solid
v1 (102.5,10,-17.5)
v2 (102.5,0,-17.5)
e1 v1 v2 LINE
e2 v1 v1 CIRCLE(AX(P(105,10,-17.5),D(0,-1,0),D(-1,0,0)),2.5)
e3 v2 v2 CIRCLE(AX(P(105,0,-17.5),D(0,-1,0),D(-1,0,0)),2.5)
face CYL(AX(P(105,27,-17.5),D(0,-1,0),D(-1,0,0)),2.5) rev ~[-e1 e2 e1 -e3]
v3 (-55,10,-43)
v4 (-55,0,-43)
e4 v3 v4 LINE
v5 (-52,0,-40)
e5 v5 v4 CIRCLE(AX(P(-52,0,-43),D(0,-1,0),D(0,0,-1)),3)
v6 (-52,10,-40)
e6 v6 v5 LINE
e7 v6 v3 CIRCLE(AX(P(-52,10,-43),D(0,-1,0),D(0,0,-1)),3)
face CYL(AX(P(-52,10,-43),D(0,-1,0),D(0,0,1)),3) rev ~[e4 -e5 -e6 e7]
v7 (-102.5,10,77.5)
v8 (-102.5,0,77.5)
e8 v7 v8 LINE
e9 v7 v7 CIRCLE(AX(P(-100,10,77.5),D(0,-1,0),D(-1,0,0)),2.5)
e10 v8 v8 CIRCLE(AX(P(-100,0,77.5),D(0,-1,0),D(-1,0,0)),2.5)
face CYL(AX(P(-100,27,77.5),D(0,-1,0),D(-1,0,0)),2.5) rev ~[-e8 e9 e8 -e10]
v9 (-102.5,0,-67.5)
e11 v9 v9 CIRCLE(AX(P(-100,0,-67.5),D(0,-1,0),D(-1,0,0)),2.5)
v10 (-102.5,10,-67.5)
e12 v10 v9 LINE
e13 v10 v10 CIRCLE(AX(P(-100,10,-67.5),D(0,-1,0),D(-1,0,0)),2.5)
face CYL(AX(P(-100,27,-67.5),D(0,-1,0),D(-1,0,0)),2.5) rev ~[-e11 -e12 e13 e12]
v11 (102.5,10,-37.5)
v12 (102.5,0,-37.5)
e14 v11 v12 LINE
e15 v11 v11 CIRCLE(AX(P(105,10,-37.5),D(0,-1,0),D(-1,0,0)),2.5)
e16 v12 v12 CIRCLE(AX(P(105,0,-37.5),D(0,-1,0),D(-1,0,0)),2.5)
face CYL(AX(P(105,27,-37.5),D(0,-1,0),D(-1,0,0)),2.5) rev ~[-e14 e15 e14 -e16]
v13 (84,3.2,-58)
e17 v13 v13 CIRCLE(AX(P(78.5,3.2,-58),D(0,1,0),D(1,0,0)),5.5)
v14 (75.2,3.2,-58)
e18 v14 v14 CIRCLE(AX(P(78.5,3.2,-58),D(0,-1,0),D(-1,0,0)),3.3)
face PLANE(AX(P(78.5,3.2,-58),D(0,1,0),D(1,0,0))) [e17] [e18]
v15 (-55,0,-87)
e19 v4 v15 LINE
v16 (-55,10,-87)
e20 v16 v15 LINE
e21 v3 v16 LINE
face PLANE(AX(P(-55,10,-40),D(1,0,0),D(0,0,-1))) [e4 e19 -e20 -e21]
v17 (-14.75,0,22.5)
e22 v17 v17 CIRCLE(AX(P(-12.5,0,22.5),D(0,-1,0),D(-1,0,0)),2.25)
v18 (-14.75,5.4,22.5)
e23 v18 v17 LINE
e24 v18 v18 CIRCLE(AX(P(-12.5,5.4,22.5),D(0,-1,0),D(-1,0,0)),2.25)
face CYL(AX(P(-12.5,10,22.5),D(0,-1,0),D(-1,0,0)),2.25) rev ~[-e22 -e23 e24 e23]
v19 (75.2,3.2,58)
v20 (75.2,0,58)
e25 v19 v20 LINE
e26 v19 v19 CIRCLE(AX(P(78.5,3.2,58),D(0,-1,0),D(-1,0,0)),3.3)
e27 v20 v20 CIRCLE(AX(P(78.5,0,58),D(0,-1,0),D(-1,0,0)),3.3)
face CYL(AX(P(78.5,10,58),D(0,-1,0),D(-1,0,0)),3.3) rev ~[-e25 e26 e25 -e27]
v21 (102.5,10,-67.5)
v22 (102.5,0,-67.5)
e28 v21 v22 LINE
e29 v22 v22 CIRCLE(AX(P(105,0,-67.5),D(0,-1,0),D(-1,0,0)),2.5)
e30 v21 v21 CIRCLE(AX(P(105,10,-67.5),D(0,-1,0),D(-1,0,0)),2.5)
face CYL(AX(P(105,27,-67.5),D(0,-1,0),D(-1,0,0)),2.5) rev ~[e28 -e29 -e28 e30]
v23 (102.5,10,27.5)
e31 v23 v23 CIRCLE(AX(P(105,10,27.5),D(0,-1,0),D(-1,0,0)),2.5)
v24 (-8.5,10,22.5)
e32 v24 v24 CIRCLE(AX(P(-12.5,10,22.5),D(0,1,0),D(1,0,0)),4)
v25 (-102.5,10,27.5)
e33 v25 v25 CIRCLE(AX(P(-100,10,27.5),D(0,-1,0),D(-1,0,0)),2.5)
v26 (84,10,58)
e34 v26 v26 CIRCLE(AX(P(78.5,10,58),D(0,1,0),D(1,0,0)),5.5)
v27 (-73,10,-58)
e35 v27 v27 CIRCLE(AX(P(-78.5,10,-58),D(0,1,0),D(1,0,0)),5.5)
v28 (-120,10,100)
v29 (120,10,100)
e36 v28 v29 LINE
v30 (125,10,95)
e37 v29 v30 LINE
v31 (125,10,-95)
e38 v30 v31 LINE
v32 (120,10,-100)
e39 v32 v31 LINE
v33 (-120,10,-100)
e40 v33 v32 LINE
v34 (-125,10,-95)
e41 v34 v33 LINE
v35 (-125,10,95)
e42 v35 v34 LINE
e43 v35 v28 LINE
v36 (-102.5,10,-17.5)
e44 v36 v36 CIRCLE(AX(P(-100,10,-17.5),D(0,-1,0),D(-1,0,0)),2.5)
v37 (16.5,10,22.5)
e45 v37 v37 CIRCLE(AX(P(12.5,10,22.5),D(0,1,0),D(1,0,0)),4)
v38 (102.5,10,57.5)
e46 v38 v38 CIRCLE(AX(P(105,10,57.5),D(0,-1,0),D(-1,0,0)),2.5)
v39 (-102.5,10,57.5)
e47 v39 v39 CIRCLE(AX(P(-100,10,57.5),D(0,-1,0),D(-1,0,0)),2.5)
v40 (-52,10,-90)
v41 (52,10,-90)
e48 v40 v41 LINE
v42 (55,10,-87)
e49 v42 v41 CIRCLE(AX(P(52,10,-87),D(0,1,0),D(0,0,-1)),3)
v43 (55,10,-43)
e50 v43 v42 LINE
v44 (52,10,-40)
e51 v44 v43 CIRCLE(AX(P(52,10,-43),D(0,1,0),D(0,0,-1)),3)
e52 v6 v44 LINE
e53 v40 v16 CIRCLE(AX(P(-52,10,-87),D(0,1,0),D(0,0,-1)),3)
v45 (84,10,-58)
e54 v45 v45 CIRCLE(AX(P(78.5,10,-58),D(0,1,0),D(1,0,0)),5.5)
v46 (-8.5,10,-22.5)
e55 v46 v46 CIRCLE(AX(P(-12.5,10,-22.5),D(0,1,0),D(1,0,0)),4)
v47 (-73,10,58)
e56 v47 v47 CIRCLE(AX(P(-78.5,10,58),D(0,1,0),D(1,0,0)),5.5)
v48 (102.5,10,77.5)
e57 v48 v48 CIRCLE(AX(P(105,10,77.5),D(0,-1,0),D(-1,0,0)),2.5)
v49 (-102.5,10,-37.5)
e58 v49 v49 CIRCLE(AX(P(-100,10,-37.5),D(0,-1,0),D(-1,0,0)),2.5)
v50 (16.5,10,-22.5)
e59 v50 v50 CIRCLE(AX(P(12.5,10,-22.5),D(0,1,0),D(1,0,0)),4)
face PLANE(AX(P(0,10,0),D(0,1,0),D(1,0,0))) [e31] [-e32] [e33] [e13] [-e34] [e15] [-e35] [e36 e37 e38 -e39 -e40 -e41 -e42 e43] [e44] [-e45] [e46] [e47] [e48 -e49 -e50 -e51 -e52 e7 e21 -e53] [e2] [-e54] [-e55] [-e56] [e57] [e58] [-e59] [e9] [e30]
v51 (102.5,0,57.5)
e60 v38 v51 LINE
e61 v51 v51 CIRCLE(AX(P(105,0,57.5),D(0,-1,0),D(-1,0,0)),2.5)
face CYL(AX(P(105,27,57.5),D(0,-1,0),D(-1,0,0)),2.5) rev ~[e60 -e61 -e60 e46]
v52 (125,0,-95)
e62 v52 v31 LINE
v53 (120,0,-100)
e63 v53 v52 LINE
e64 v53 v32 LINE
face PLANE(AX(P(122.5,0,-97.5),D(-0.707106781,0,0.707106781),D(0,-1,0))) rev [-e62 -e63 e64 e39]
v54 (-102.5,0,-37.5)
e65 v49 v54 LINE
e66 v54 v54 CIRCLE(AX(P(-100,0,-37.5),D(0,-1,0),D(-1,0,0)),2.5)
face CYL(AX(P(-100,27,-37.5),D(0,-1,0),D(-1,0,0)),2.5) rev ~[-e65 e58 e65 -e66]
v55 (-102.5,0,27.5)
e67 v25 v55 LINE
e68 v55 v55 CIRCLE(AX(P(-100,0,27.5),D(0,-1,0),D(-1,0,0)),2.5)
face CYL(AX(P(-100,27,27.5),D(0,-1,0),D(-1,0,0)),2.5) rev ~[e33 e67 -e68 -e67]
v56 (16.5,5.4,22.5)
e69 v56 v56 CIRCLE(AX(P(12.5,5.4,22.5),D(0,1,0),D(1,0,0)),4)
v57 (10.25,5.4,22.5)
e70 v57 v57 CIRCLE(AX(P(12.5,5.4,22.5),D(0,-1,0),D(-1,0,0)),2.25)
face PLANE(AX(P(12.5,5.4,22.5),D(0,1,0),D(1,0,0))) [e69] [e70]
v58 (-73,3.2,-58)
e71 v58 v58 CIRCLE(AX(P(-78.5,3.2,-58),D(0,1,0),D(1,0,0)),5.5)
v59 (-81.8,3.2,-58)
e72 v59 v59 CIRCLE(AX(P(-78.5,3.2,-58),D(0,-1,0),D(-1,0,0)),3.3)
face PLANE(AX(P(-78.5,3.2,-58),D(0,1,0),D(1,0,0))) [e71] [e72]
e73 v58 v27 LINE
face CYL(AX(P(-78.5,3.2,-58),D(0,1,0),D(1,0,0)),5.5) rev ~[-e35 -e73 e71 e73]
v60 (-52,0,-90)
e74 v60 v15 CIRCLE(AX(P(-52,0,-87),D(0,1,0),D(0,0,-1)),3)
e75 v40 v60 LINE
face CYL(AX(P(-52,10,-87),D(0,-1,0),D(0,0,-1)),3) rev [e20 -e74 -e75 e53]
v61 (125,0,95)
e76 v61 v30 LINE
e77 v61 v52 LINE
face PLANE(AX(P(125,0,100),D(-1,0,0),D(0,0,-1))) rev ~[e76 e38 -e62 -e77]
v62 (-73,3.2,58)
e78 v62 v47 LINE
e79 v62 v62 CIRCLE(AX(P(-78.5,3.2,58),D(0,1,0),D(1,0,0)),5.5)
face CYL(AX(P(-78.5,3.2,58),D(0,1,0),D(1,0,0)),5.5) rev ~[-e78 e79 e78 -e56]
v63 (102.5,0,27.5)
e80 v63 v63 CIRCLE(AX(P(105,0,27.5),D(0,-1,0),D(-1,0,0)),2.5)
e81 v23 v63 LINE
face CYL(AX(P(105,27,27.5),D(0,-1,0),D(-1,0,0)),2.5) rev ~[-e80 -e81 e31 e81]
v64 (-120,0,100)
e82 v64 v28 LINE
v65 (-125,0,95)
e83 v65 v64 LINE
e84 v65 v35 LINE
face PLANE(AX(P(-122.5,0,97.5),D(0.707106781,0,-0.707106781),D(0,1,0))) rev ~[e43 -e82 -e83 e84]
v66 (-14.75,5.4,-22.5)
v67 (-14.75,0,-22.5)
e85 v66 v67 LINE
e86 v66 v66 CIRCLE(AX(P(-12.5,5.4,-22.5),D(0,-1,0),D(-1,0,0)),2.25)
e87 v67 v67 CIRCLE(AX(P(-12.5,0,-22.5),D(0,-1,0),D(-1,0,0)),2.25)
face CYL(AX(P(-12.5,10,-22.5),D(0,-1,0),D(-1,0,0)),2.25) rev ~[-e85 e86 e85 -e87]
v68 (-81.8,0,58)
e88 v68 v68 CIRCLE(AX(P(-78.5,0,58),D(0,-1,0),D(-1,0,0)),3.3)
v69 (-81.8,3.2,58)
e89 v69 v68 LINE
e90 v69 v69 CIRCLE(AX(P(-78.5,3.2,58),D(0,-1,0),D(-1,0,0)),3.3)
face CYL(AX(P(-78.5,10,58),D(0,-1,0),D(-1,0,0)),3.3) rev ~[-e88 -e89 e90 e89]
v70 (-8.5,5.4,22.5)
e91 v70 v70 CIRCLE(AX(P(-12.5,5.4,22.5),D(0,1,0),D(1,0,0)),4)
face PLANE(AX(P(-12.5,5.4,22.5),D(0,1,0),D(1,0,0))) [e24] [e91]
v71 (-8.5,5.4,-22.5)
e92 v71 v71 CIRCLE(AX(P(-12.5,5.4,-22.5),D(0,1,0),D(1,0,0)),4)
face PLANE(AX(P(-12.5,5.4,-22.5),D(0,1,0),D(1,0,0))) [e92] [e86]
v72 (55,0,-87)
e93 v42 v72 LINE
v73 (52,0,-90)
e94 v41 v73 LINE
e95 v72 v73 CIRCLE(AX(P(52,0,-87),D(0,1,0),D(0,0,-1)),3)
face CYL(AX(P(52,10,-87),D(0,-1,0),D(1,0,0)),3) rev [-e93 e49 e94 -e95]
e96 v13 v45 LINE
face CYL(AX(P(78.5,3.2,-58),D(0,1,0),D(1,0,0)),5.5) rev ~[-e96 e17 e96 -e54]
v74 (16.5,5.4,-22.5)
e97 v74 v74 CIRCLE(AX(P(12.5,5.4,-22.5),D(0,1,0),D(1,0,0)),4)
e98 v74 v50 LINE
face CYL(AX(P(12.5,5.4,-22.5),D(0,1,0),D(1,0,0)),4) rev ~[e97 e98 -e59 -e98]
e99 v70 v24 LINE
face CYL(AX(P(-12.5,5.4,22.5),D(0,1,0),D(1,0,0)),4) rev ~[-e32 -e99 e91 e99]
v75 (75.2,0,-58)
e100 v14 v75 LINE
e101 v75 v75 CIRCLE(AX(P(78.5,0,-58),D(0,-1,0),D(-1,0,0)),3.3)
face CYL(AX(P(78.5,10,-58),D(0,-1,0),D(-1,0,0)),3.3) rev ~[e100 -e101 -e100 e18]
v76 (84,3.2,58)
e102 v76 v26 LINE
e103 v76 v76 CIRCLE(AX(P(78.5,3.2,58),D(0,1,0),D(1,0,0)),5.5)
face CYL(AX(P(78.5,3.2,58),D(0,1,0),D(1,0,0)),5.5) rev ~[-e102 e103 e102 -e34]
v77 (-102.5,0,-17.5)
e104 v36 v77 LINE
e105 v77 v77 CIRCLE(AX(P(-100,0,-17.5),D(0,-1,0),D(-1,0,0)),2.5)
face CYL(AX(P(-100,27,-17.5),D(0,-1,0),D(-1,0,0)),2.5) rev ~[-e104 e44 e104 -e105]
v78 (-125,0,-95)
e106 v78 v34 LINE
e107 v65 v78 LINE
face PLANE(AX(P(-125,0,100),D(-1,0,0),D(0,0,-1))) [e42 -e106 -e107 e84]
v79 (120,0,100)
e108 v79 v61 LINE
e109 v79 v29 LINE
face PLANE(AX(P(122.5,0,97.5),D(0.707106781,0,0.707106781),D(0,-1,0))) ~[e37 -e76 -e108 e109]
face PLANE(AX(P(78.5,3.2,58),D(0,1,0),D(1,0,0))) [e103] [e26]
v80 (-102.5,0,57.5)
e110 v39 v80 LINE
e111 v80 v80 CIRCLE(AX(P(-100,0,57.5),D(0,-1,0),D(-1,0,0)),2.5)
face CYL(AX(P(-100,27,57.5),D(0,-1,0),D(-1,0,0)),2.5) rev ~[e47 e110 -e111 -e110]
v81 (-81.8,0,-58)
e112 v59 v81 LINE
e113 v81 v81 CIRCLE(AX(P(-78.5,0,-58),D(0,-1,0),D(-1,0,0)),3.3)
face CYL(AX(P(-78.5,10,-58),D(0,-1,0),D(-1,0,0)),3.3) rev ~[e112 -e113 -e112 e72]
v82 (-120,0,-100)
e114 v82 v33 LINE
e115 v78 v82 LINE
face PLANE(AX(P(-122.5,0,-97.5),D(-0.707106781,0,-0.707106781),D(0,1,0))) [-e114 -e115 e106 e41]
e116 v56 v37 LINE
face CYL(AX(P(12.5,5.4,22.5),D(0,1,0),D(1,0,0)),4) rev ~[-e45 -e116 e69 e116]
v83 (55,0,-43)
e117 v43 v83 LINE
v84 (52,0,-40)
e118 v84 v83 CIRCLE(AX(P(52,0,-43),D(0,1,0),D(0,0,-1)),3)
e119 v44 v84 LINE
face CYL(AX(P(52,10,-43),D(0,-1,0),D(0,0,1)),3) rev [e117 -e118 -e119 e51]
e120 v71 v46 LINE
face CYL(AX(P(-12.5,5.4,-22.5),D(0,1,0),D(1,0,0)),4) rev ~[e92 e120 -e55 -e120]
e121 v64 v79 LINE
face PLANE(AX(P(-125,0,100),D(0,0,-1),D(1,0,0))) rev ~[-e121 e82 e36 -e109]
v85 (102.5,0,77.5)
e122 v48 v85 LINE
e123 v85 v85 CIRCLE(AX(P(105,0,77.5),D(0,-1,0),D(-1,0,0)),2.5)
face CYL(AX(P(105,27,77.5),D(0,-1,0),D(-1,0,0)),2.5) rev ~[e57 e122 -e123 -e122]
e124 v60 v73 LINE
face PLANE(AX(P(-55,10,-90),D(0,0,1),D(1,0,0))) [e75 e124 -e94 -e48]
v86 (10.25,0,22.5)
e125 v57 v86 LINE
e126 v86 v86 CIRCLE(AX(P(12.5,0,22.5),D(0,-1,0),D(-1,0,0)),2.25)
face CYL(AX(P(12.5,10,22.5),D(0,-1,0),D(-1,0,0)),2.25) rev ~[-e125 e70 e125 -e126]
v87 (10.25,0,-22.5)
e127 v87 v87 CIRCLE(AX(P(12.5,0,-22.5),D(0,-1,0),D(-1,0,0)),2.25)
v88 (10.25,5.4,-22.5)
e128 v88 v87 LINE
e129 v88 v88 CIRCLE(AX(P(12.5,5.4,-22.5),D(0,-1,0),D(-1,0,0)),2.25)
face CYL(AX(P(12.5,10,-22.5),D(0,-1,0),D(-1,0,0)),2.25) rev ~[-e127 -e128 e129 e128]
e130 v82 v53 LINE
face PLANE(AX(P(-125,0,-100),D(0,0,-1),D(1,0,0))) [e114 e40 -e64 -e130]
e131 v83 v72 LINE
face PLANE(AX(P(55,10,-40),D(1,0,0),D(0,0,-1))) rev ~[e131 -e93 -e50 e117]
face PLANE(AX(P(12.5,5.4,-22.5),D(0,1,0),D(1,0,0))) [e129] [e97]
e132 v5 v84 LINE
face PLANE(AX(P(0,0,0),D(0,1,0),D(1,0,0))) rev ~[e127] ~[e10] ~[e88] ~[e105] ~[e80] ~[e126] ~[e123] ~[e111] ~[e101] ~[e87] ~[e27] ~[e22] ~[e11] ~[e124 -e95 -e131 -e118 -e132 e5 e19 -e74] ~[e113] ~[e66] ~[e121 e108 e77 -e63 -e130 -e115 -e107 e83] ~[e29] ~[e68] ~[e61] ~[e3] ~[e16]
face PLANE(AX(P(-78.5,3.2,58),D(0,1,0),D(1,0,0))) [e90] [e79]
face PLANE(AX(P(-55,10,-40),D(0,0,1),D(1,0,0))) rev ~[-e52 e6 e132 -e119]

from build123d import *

# Parameters (mm, degrees)
SKETCH1_W                                            = 250
SKETCH1_H                                            = 200
BOSS_EXTRUDE1_DEPTH                                  = 10
M6_TAPPED_HOLE1_D                                    = 5
M6_TAPPED_HOLE1_DEPTH                                = 17
M6_TAPPED_HOLE1_TIP                                  = 1.502151548
SKETCH6_W                                            = 110
SKETCH6_H                                            = 50
CUT_EXTRUDE2_DEPTH                                   = 161.390149323
FILLET1_R                                            = 3
CHAMFER1_SIZE                                        = 5
CBORE_FOR_M6_HEXAGON_SOCKET_HEAD_CAP_SCR_D           = 6.6
CBORE_FOR_M6_HEXAGON_SOCKET_HEAD_CAP_SCR_CBORE_D     = 11
CBORE_FOR_M6_HEXAGON_SOCKET_HEAD_CAP_SCR_CBORE_DEPTH = 6.8
CBORE_FOR_M4_HEXAGON_SOCKET_HEAD_CAP_SCR_D           = 4.5
CBORE_FOR_M4_HEXAGON_SOCKET_HEAD_CAP_SCR_CBORE_D     = 8
CBORE_FOR_M4_HEXAGON_SOCKET_HEAD_CAP_SCR_CBORE_DEPTH = 4.6


with BuildPart() as part:
    # Sketch1 → Boss-Extrude1 (new body)
    with BuildSketch(Plane(origin=(0, 0, 0), x_dir=(1, 0, 0), z_dir=(0, 1, 0))):
        Rectangle(SKETCH1_W, SKETCH1_H)
    extrude(amount=BOSS_EXTRUDE1_DEPTH)

    # M6 Tapped Hole1
    with Locations(Plane(origin=(0, 10, 0), x_dir=(1, 0, 0), z_dir=(0, 1, 0))):
        with Locations((105, -77.5), (-100, -77.5), (-100, 17.5), (105, 17.5), (-100, 37.5), (-100, 67.5), (105, 37.5), (105, 67.5), (-100, -57.5), (-100, -27.5), (105, -57.5), (105, -27.5)):
            Hole(M6_TAPPED_HOLE1_D / 2, depth=M6_TAPPED_HOLE1_DEPTH)
            with Locations((0, 0, -(M6_TAPPED_HOLE1_DEPTH + M6_TAPPED_HOLE1_TIP / 2))):  # 118° drill point
                Cone(0, M6_TAPPED_HOLE1_D / 2, M6_TAPPED_HOLE1_TIP, mode=Mode.SUBTRACT)

    # Sketch6 → Cut-Extrude2 (cut, through all)
    with BuildSketch(Plane(origin=(0, 10, 0), x_dir=(1, 0, 0), z_dir=(0, 1, 0))):
        with Locations((0, 65)):
            Rectangle(SKETCH6_W, SKETCH6_H)
    extrude(amount=-CUT_EXTRUDE2_DEPTH, mode=Mode.SUBTRACT)

    # Fillet1
    fillet1_edges = [part.edges().sort_by_distance(p)[0] for p in [
        (-55, 5, -40),
        (-55, 5, -90),
        (55, 5, -90),
        (55, 5, -40),
    ]]
    fillet(fillet1_edges, radius=FILLET1_R)

    # Chamfer1
    chamfer1_edges = [part.edges().sort_by_distance(p)[0] for p in [
        (125, 5, 100),
        (-125, 5, 100),
        (-125, 5, -100),
        (125, 5, -100),
    ]]
    chamfer(chamfer1_edges, length=CHAMFER1_SIZE)

    # CBORE for M6 Hexagon socket head cap screws1 (through all)
    with Locations(Plane(origin=(0, 10, 0), x_dir=(1, 0, 0), z_dir=(0, 1, 0))):
        with Locations((-78.5, 58), (78.5, 58), (78.5, -58), (-78.5, -58)):
            CounterBoreHole(CBORE_FOR_M6_HEXAGON_SOCKET_HEAD_CAP_SCR_D / 2, CBORE_FOR_M6_HEXAGON_SOCKET_HEAD_CAP_SCR_CBORE_D / 2, CBORE_FOR_M6_HEXAGON_SOCKET_HEAD_CAP_SCR_CBORE_DEPTH)

    # CBORE for M4 Hexagon socket head cap screws1 (through all)
    with Locations(Plane(origin=(0, 10, 0), x_dir=(1, 0, 0), z_dir=(0, 1, 0))):
        with Locations((-12.5, 22.5), (12.5, 22.5), (12.5, -22.5), (-12.5, -22.5)):
            CounterBoreHole(CBORE_FOR_M4_HEXAGON_SOCKET_HEAD_CAP_SCR_D / 2, CBORE_FOR_M4_HEXAGON_SOCKET_HEAD_CAP_SCR_CBORE_D / 2, CBORE_FOR_M4_HEXAGON_SOCKET_HEAD_CAP_SCR_CBORE_DEPTH)


solid = part.part
